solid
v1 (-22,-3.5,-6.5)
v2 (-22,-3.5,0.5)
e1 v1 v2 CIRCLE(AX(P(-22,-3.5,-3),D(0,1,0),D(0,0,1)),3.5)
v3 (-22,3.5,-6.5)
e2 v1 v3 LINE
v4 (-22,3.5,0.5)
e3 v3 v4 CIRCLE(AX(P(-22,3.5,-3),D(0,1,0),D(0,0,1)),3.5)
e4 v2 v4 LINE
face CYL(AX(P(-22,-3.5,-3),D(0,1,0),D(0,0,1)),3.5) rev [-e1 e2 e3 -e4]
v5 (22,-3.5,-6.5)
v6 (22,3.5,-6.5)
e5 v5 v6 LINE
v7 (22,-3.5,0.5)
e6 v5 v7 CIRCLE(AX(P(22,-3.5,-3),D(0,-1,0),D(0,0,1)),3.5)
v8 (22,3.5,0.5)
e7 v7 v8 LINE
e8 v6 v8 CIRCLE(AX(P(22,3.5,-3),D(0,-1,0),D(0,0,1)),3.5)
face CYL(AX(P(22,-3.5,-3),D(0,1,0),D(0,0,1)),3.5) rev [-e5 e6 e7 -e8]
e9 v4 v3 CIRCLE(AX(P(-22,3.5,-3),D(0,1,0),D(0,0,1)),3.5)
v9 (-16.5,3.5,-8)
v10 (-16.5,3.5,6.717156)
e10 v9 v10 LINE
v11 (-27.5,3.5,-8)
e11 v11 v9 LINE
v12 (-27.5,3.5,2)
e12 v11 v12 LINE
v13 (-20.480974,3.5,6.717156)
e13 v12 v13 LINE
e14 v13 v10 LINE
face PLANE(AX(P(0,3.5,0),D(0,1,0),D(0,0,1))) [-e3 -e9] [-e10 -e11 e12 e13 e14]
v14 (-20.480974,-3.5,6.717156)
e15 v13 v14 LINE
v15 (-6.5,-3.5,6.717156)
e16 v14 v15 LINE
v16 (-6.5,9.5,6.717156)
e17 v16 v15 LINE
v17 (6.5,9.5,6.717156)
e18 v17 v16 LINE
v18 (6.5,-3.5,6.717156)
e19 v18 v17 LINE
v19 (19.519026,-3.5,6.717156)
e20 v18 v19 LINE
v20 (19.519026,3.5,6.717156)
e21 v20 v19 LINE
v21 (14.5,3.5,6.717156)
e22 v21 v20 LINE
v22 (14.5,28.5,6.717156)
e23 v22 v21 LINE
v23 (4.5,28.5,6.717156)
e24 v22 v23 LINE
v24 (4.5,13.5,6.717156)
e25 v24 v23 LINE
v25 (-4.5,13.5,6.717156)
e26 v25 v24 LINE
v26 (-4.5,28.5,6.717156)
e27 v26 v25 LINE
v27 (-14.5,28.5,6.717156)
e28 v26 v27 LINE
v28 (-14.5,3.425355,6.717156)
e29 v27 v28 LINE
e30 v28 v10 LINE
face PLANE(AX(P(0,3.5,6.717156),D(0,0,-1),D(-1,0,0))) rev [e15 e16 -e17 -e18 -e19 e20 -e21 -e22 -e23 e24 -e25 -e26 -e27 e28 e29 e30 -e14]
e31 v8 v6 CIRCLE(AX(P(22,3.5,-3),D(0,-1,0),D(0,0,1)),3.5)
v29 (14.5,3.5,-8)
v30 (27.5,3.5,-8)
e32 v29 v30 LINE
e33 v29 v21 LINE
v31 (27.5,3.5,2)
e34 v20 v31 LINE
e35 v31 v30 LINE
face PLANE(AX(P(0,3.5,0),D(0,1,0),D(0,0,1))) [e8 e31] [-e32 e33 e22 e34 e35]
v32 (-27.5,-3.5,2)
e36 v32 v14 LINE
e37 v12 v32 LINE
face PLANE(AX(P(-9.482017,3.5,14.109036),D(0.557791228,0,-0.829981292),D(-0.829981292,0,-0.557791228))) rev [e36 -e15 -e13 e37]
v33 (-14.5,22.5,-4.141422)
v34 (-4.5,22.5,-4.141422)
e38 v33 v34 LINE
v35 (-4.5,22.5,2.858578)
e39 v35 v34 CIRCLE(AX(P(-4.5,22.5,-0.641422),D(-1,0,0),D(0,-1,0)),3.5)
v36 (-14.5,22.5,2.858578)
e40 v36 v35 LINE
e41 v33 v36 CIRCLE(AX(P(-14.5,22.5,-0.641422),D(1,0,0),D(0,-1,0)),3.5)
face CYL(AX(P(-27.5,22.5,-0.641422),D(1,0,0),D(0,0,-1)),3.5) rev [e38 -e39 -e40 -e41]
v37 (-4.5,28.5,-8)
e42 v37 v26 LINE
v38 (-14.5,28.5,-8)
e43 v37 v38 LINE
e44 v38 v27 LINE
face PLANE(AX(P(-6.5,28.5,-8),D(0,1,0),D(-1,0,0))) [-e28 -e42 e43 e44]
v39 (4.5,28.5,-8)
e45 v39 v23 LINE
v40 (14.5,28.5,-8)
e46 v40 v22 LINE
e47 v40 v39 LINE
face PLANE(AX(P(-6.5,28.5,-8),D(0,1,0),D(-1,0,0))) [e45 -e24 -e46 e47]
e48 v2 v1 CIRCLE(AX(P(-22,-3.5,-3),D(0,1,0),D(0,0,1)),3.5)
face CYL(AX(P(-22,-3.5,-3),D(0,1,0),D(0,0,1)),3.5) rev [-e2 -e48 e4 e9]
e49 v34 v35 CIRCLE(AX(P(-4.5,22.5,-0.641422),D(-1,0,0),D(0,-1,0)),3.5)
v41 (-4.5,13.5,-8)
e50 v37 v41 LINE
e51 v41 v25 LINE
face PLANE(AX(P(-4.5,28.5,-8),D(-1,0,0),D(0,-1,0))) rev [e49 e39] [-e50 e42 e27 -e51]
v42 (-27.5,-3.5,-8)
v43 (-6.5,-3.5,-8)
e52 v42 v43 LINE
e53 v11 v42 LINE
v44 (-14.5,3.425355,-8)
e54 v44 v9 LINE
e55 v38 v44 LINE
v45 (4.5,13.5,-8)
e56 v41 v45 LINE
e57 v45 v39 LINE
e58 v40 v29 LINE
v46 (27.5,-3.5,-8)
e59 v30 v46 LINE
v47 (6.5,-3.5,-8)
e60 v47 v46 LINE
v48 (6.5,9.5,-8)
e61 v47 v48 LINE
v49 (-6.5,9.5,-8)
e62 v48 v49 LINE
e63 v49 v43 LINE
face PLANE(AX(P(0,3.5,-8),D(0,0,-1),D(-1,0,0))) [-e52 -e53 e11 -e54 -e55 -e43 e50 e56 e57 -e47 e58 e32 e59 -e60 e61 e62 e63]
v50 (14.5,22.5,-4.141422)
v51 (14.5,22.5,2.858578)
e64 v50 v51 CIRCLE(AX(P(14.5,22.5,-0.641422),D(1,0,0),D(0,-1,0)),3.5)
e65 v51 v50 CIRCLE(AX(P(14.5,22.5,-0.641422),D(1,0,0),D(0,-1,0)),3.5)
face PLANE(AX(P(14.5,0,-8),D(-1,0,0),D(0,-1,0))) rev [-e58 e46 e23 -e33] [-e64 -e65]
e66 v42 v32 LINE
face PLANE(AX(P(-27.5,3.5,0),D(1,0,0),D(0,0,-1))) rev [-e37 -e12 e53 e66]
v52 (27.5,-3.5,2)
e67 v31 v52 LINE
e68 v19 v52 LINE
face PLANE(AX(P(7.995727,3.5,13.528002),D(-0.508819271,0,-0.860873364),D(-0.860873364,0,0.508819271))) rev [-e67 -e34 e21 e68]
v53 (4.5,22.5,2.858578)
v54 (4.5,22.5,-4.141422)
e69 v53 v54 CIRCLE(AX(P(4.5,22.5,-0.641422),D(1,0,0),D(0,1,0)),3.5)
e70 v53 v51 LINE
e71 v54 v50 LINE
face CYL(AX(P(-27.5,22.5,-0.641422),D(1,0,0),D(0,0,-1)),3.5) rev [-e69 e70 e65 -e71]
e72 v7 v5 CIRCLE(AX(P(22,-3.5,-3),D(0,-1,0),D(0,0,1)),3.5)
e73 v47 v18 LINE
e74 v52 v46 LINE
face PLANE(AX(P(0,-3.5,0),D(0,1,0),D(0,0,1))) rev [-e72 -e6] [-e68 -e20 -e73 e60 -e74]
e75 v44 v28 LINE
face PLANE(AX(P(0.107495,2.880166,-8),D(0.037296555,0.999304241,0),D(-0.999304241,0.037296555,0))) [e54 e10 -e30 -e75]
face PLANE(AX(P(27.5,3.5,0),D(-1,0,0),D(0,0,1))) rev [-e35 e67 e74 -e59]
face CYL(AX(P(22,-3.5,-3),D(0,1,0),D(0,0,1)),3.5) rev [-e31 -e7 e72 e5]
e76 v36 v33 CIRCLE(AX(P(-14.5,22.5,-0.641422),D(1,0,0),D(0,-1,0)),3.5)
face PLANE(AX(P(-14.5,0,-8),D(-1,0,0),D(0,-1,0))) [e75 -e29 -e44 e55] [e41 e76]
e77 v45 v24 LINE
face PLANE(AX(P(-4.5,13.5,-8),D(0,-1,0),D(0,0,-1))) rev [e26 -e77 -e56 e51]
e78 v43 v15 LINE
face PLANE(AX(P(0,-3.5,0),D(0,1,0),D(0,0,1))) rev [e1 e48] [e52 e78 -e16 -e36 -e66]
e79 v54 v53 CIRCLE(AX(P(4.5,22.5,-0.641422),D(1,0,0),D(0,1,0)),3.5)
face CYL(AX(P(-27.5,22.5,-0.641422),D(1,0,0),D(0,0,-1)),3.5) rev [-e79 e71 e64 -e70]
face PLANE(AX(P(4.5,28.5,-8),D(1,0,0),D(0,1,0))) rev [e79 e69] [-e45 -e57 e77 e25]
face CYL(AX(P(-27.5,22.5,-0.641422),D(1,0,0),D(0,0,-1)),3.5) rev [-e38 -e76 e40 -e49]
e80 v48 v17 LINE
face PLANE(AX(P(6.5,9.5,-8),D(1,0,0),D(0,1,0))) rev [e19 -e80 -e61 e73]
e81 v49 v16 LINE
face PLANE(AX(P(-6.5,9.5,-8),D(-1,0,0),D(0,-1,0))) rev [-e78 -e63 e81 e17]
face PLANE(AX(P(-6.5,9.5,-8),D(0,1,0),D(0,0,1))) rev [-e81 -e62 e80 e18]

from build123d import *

# Parameters (mm, degrees)
BASE_PLATE_55X7_DEPTH         = 3.5
FRONT_NOTCH_SKETCH_W          = 13
FRONT_NOTCH_SKETCH_H          = 9.412383513
FRONT_NOTCH_13X6_5_DEPTH      = 32.38621781
UPRIGHT_A_SKETCH_W            = 10
UPRIGHT_A_SKETCH_H            = 32
UPRIGHT_A_10X32_DEPTH         = 14.717156
UPRIGHT_B_SKETCH_W            = 10
UPRIGHT_B_SKETCH_H            = 32
UPRIGHT_B_10X32_DEPTH         = 14.717156
UPRIGHT_A_HOLE_SKETCH_R       = 3.5
UPRIGHT_A_HOLE_DEPTH          = 39.016443898
INFILL_BOSS_SKETCH_W          = 13
INFILL_BOSS_SKETCH_H          = 32
INFILL_BOSS_DEPTH             = 14.717156
REAR_NOTCH_SKETCH_W           = 13
REAR_NOTCH_SKETCH_H           = 13
REAR_NOTCH_13X6_5_DEPTH       = 43.250380835
SLOT_CUT_SKETCH_W             = 9
SLOT_CUT_SKETCH_H             = 15
SLOT_CUT_DEPTH                = 43.250380835
UPRIGHT_B_HOLE_SKETCH_R       = 3.5
UPRIGHT_B_HOLE_DEPTH          = 54.030651577
FLANGE_PROFILE_CUT_A_SKETCH_W = 2
FLANGE_PROFILE_CUT_A_SKETCH_H = 25
FLANGE_PROFILE_CUT_A_DEPTH    = 43.250380835
FLANGE_PROFILE_CUT_B_DEPTH    = 43.250380835


with BuildPart() as part:
    # Base Plate Sketch → Base Plate 55x7 (new, symmetric)
    with BuildSketch(Plane(origin=(0, 0, 0), x_dir=(1, 0, 0), z_dir=(0, 1, 0))):
        Polygon((-20.480974443, -6.717155582), (19.519025557, -6.717155582), (27.5, -2), (27.5, 8), (-27.5, 8), (-27.5, -2), align=None)
    extrude(amount=BASE_PLATE_55X7_DEPTH, both=True)

    # Front Notch Sketch → Front Notch 13x6.5 (cut, through all)
    with BuildSketch(Plane.XY.offset(6.717155582)):
        with Locations((0, -0.276834809)):
            Rectangle(FRONT_NOTCH_SKETCH_W, FRONT_NOTCH_SKETCH_H)
    extrude(amount=-FRONT_NOTCH_13X6_5_DEPTH, mode=Mode.SUBTRACT)


with BuildPart() as front_notch_13x6_5_piece_1:
    # of the separate pieces the step leaves, piece 1, a body of its own (front_notch_13x6_5_pieces)
    add(part.part.solids().sort_by_distance((-20.480974443, 3.5, 6.717155582))[0])

    # Upright A Sketch → Upright A 10x32 (add)
    with BuildSketch(Plane.XY.offset(6.717155582)):
        with Locations((-11.5, 12.5)):
            Rectangle(UPRIGHT_A_SKETCH_W, UPRIGHT_A_SKETCH_H)
    extrude(amount=-UPRIGHT_A_10X32_DEPTH)


with BuildPart() as front_notch_13x6_5_piece_2:
    # of the separate pieces the step leaves, piece 2, a body of its own (front_notch_13x6_5_pieces)
    add(part.part.solids().sort_by_distance((6.5, 3.5, 6.717155582))[0])

    # Upright B Sketch → Upright B 10x32 (add)
    with BuildSketch(Plane.XY.offset(6.717155582)):
        with Locations((11.5, 12.5)):
            Rectangle(UPRIGHT_B_SKETCH_W, UPRIGHT_B_SKETCH_H)
    extrude(amount=-UPRIGHT_B_10X32_DEPTH)


with BuildPart() as upright_a_hole_tool:
    # Upright A Hole Sketch → Upright A Hole (new, through all)
    with BuildSketch(Plane(origin=(0, 3.5, 0), x_dir=(1, 0, 0), z_dir=(0, 1, 0))):
        with Locations(Location((-22, 3, 0), (0, 0, 270))):
            Circle(UPRIGHT_A_HOLE_SKETCH_R)
        with Locations(Location((22, 3, 0), (0, 0, 270))):
            Circle(UPRIGHT_A_HOLE_SKETCH_R)
    extrude(amount=-UPRIGHT_A_HOLE_DEPTH)


with BuildPart() as front_notch_13x6_5_piece_1_1:
    add(front_notch_13x6_5_piece_1.part)

    # Upright A Hole: cut by upright_a_hole_tool
    add(upright_a_hole_tool.part, mode=Mode.SUBTRACT)



with BuildPart() as front_notch_13x6_5_piece_2_1:
    add(front_notch_13x6_5_piece_2.part)

    # Upright A Hole: cut by upright_a_hole_tool
    add(upright_a_hole_tool.part, mode=Mode.SUBTRACT)


with BuildPart() as front_notch_13x6_5_piece_1_2:
    add(front_notch_13x6_5_piece_1_1.part)

    add(front_notch_13x6_5_piece_2_1.part)  # Infill Boss merges Front Notch 13x6.5 piece 2
    # Infill Boss Sketch → Infill Boss (add, through all)
    with BuildSketch(Plane.XY.offset(6.717155582)):
        with Locations((0, 12.5)):
            Rectangle(INFILL_BOSS_SKETCH_W, INFILL_BOSS_SKETCH_H)
    extrude(amount=-INFILL_BOSS_DEPTH)

    # Rear Notch Sketch → Rear Notch 13x6.5 (cut, through all)
    with BuildSketch(Plane.XY.offset(6.717155582)):
        with Locations((0, 3)):
            Rectangle(REAR_NOTCH_SKETCH_W, REAR_NOTCH_SKETCH_H)
    extrude(amount=-REAR_NOTCH_13X6_5_DEPTH, mode=Mode.SUBTRACT)

    # Slot Cut Sketch → Slot Cut (cut, through all)
    with BuildSketch(Plane.XY.offset(6.717155582)):
        with Locations((0, 21)):
            Rectangle(SLOT_CUT_SKETCH_W, SLOT_CUT_SKETCH_H)
    extrude(amount=-SLOT_CUT_DEPTH, mode=Mode.SUBTRACT)

    # Upright B Hole Sketch → Upright B Hole (cut, through all)
    with BuildSketch(Plane(origin=(16.5, 0, 0), x_dir=(0, 0, -1), z_dir=(1, 0, 0))):
        with Locations((0.641422209, 22.5)):
            Circle(UPRIGHT_B_HOLE_SKETCH_R)
    extrude(amount=-UPRIGHT_B_HOLE_DEPTH, mode=Mode.SUBTRACT)

    # Flange Profile Cut A Sketch → Flange Profile Cut A (cut, through all)
    with BuildSketch(Plane.XY.offset(6.717155582)):
        with Locations((15.5, 16)):
            Rectangle(FLANGE_PROFILE_CUT_A_SKETCH_W, FLANGE_PROFILE_CUT_A_SKETCH_H)
    extrude(amount=-FLANGE_PROFILE_CUT_A_DEPTH, mode=Mode.SUBTRACT)

    # Flange Profile Cut B Sketch → Flange Profile Cut B (cut, through all)
    with BuildSketch(Plane.XY.offset(6.717155582)):
        Polygon((-14.5, 3.425354954), (-14.5, 28.5), (-16.5, 28.5), (-16.5, 3.5), align=None)
    extrude(amount=-FLANGE_PROFILE_CUT_B_DEPTH, mode=Mode.SUBTRACT)


solid = front_notch_13x6_5_piece_1_2.part
